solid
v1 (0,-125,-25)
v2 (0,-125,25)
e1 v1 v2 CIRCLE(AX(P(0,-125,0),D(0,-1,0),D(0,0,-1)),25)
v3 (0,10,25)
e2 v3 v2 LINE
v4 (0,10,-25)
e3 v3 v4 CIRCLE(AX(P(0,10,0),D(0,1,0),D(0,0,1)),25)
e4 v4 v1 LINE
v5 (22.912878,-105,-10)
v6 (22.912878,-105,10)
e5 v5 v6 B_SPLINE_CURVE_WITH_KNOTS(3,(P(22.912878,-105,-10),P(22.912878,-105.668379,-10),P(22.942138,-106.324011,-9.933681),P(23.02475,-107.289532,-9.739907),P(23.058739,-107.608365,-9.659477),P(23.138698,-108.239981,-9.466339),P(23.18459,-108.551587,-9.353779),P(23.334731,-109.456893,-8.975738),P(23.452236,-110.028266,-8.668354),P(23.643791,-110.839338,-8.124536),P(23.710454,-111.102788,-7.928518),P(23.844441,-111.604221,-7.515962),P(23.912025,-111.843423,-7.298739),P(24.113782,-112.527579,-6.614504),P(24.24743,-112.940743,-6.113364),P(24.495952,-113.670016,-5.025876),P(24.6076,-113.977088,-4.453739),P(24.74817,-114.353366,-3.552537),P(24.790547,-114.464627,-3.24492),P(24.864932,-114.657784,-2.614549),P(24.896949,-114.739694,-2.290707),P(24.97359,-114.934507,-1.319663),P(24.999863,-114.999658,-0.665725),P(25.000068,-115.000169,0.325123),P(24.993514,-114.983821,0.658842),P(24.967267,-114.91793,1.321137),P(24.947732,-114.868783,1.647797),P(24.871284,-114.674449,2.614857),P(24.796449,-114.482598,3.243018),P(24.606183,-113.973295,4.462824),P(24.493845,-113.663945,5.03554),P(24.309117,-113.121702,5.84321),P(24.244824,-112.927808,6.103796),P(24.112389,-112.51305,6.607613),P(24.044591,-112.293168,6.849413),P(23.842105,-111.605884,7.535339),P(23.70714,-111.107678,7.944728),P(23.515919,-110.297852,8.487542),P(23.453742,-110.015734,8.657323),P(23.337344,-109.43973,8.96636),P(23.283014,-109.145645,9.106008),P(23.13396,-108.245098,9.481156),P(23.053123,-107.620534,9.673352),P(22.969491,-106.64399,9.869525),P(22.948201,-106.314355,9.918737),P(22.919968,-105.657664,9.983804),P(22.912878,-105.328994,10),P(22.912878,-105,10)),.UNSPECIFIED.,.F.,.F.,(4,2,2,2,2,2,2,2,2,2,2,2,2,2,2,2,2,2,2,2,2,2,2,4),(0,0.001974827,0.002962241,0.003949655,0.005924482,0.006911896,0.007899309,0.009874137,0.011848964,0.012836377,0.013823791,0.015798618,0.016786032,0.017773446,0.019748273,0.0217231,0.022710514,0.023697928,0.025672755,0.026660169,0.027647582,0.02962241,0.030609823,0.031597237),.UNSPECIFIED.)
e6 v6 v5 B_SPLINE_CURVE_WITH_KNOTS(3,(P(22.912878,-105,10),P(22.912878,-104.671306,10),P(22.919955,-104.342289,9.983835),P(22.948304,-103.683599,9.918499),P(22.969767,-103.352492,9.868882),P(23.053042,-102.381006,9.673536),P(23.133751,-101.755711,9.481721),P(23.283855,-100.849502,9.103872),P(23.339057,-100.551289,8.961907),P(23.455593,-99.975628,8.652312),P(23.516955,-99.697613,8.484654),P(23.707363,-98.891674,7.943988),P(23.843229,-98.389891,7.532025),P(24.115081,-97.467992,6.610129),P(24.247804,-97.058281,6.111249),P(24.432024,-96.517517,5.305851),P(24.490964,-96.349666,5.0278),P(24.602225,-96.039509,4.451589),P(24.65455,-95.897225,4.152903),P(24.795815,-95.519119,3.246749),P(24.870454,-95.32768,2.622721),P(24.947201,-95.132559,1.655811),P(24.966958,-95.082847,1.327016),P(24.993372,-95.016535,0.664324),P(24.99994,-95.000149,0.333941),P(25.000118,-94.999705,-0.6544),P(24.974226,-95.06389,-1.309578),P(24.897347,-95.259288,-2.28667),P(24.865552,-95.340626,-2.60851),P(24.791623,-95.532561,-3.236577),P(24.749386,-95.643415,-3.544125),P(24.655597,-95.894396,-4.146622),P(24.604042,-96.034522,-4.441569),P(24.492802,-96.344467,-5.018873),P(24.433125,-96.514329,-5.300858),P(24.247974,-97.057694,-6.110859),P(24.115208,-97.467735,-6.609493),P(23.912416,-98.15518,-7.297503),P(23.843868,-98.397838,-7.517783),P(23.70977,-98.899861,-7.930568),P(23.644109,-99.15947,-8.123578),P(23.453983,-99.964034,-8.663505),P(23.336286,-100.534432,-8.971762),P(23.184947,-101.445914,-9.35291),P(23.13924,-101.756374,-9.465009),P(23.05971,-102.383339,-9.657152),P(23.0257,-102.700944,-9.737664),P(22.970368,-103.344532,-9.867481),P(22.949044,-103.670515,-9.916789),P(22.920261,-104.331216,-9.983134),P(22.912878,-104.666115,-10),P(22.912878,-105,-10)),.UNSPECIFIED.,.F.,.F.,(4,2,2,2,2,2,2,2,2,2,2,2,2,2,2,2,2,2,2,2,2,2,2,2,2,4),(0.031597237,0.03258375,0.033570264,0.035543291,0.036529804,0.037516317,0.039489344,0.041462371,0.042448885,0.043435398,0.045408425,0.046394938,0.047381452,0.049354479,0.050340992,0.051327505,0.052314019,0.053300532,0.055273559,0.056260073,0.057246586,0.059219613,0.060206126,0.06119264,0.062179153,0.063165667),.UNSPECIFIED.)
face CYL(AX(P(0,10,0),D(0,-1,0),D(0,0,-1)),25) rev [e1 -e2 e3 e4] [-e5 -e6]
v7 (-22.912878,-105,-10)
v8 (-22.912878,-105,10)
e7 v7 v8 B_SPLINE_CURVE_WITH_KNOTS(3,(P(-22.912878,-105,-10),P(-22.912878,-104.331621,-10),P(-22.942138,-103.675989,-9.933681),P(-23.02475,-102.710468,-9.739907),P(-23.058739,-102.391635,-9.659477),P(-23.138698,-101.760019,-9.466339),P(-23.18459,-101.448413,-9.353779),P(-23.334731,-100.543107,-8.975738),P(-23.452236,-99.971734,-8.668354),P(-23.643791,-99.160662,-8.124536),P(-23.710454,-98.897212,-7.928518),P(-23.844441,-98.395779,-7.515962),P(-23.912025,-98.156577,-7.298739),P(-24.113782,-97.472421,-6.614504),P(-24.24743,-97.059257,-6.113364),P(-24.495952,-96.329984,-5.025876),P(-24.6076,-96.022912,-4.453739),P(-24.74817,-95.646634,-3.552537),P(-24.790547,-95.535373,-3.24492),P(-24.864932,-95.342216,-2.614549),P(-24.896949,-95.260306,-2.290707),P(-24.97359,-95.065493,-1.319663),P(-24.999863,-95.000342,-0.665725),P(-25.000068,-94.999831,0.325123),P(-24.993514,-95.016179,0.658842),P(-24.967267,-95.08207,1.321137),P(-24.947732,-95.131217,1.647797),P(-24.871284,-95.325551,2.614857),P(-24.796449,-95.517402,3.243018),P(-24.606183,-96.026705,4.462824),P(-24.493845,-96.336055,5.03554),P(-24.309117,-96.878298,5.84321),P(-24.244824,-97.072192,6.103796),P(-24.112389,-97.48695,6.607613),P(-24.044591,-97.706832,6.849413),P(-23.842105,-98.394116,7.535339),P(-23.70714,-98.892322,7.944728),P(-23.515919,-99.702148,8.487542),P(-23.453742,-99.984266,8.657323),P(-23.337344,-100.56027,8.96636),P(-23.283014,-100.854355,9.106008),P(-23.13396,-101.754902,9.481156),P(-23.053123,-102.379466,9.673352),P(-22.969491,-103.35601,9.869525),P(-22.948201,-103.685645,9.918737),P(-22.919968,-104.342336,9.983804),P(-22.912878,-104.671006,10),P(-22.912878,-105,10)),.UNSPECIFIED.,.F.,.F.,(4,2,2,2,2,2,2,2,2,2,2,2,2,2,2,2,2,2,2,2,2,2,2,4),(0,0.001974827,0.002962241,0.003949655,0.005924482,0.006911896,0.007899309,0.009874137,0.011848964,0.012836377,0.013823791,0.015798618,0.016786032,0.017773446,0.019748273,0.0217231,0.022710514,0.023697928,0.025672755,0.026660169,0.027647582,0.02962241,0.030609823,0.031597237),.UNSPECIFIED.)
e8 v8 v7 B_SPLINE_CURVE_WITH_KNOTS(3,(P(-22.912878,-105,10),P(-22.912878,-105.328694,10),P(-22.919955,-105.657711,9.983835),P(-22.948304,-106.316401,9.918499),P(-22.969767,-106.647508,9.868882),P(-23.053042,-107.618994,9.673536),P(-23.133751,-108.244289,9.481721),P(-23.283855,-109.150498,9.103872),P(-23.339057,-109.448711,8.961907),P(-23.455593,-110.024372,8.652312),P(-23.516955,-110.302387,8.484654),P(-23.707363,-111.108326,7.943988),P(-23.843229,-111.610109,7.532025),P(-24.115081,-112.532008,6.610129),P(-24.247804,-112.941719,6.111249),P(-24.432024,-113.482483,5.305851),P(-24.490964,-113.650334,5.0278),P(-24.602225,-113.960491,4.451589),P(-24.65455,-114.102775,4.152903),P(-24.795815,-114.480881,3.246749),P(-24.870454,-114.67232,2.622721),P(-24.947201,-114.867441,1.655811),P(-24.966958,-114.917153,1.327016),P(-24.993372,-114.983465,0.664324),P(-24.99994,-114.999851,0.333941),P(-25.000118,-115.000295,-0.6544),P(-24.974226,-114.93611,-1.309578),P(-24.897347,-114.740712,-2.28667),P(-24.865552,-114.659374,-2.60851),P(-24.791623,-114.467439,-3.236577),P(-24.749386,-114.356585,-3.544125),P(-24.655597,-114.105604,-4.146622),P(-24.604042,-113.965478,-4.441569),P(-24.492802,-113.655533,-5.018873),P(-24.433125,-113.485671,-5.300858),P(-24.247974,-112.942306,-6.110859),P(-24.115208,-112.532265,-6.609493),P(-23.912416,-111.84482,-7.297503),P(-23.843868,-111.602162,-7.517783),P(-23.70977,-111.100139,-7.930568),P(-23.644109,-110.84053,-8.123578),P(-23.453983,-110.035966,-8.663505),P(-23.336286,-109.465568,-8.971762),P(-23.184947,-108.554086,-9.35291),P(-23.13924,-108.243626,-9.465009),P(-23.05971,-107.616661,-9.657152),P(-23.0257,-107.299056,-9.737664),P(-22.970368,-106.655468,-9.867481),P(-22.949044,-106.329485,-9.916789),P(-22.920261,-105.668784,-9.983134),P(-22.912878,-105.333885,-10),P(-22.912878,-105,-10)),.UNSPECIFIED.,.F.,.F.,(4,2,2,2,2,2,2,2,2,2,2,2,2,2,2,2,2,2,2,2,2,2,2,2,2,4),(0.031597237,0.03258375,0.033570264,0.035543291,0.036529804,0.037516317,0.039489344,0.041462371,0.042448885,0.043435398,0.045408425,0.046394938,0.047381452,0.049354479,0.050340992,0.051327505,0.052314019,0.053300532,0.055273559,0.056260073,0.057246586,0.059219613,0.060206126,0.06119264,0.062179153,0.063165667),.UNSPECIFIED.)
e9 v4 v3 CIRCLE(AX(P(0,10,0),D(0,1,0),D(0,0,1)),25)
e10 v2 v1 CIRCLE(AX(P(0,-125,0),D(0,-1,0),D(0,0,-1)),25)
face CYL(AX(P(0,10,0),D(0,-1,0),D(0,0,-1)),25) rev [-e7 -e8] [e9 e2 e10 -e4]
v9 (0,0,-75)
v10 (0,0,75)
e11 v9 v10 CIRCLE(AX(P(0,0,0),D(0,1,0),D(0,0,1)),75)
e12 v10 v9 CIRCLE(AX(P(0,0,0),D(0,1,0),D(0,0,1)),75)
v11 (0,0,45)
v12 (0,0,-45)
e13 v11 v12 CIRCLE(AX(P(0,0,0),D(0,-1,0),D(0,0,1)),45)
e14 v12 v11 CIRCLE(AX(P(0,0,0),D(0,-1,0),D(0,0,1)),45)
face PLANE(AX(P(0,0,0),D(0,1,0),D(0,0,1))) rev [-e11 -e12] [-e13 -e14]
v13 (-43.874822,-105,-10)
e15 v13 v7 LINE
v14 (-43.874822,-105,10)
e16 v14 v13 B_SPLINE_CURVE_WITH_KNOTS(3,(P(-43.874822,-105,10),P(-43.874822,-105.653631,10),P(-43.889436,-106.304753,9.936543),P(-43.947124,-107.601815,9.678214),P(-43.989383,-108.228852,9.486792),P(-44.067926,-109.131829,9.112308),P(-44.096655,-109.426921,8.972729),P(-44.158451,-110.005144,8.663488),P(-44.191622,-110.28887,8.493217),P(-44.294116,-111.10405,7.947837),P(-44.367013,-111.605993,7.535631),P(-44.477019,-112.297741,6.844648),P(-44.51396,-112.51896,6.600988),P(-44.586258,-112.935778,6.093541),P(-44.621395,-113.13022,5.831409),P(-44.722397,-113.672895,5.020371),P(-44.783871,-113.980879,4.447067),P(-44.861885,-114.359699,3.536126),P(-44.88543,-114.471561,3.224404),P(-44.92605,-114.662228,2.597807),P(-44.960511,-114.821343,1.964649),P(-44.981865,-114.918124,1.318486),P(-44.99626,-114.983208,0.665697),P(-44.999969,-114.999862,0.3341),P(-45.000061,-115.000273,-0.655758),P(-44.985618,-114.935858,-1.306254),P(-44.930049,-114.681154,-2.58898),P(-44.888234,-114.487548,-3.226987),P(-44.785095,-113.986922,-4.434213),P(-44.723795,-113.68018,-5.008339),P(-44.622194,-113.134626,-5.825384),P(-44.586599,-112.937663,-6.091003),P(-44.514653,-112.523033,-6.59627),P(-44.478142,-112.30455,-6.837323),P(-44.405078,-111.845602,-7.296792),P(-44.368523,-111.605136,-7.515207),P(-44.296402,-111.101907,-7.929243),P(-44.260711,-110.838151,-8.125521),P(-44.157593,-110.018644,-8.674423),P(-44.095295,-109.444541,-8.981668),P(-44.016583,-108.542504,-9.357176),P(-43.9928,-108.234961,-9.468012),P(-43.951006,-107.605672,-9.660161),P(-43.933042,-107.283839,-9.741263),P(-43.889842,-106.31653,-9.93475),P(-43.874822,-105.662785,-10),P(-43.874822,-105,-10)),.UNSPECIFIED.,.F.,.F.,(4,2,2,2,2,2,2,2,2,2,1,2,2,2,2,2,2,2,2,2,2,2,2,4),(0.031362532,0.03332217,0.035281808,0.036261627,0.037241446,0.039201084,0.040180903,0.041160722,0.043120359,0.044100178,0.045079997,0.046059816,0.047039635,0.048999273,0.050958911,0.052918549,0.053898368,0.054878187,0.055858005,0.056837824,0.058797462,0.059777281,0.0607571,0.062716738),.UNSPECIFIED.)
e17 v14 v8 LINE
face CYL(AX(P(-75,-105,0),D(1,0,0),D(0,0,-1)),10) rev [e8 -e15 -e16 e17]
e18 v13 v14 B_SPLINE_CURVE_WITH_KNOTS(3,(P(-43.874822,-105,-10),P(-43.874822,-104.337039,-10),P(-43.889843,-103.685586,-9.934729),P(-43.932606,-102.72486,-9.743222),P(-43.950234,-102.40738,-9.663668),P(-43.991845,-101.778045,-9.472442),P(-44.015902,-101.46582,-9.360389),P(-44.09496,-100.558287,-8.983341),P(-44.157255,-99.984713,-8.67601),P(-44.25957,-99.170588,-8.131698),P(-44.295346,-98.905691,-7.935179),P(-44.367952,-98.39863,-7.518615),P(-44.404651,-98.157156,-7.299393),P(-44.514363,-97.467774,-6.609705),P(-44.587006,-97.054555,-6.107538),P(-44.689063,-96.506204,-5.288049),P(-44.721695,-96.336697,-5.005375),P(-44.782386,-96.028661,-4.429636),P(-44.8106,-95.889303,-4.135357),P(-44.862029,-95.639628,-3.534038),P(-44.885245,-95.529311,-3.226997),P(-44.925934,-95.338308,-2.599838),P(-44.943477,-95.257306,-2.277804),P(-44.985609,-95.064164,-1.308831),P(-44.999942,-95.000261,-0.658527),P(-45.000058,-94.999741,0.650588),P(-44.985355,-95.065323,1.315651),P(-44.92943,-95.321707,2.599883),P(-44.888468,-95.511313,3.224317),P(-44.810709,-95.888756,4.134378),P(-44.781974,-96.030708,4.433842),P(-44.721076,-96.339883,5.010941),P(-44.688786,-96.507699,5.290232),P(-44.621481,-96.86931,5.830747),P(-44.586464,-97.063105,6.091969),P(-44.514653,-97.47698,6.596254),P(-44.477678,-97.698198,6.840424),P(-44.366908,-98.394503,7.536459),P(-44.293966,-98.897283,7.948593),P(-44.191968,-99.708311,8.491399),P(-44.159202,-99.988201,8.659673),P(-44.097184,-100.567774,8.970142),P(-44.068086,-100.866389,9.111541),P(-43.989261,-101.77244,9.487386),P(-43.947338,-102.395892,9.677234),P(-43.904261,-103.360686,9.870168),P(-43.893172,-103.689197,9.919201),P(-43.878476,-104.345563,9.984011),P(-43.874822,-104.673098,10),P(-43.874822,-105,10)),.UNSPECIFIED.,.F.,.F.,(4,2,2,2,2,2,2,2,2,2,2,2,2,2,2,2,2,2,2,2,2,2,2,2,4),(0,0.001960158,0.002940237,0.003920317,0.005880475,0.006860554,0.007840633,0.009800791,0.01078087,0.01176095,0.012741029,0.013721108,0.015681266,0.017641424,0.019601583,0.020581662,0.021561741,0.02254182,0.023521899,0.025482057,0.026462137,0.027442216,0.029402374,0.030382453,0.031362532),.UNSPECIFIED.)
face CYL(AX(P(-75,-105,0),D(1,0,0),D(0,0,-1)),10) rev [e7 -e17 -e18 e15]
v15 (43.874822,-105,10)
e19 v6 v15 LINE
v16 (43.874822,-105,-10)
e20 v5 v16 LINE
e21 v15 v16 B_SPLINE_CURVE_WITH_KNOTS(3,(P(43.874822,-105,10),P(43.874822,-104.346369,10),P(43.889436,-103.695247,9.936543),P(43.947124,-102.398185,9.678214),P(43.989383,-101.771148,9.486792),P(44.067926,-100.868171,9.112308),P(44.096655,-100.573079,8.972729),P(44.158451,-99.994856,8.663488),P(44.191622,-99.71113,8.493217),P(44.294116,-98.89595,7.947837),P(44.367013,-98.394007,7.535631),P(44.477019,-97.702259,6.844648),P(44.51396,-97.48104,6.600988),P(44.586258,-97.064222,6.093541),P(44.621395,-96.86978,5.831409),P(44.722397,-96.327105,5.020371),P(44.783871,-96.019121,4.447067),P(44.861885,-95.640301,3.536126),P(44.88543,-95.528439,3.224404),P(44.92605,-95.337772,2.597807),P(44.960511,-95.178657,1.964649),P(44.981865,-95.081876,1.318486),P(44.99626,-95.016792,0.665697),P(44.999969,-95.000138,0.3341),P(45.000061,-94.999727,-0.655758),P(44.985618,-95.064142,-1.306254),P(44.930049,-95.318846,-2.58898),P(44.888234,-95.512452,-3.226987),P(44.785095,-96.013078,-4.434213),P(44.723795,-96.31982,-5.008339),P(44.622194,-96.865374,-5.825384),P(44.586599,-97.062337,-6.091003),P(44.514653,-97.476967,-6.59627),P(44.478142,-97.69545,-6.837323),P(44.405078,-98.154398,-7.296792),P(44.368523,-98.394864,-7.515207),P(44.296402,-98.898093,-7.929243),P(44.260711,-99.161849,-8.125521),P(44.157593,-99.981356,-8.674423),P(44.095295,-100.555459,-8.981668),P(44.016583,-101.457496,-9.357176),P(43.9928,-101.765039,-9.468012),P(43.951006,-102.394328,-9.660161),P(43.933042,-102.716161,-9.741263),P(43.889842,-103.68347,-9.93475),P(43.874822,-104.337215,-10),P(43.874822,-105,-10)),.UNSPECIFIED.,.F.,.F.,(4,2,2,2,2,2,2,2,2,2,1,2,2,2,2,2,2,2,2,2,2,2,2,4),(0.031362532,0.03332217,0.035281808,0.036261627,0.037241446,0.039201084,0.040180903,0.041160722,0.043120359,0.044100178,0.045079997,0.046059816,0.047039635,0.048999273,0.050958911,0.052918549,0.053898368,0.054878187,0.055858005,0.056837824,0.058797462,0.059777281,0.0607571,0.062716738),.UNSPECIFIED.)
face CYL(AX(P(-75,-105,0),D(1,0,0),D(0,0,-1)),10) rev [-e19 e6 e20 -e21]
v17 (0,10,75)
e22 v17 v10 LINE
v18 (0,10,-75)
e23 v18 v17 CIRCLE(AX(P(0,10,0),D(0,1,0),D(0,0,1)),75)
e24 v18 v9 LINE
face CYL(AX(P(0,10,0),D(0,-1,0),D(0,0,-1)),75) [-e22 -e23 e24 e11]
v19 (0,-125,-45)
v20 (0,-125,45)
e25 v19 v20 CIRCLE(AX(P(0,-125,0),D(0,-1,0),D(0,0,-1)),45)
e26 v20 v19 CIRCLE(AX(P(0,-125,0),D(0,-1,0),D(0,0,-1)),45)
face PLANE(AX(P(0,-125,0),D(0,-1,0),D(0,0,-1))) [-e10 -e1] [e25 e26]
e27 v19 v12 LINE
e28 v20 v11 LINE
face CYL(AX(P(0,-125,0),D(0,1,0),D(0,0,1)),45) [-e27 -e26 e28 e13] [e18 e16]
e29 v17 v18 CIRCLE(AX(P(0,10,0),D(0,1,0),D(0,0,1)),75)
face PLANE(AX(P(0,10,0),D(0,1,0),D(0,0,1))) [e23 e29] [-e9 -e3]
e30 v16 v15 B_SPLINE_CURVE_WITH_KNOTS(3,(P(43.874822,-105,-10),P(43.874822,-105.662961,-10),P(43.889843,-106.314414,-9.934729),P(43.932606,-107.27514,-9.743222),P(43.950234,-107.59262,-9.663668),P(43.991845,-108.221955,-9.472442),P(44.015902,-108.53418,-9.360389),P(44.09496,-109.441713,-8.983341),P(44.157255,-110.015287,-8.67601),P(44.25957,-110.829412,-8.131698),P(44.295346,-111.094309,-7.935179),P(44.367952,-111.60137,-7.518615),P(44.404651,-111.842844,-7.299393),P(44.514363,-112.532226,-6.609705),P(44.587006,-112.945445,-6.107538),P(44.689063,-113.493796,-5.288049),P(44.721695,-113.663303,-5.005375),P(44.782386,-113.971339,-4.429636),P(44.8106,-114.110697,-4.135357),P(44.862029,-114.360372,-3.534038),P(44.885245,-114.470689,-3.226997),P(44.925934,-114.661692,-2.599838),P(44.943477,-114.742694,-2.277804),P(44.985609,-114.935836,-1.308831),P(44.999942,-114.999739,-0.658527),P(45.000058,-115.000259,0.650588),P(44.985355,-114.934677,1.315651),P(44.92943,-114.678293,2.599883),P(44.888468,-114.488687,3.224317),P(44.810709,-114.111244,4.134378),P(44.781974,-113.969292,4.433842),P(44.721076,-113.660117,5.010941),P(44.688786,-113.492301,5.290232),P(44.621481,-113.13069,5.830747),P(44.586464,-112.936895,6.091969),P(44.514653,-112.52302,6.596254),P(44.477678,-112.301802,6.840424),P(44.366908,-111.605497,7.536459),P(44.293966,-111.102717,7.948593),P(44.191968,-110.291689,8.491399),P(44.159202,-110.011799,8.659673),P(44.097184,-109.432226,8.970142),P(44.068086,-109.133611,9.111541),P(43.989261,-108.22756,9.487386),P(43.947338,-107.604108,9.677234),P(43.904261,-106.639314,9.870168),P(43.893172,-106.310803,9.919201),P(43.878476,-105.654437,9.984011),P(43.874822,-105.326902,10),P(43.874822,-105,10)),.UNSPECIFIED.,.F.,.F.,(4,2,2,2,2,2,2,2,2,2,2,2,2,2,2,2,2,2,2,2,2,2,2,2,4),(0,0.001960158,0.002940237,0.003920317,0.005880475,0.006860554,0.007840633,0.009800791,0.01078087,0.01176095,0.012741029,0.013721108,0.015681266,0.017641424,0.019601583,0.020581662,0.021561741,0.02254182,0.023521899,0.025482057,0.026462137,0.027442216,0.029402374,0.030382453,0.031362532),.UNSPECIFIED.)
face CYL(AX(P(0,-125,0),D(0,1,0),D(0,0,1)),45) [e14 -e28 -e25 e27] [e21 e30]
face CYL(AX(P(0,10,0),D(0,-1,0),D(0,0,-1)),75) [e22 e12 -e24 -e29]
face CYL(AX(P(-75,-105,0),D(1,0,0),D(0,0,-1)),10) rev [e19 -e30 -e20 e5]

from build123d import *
from build123d.topology import SkipClean

# Parameters (mm, degrees)
SKETCH2_R               = 75
SKETCH2_R_2             = 25
BOSS_EXTRUDE1_DEPTH     = 10
BOSS_EXTRUDE2_START     = 125
SKETCH3_R               = 45
SKETCH3_R_2             = 25
BOSS_EXTRUDE2_DEPTH     = 125
CUT_EXTRUDE1_DEPTH      = 164.935963108
CUT_EXTRUDE1_DEPTH_BACK = 164.935963108
SKETCH4_R               = 10


with BuildPart() as part:
    # Sketch2 → Boss-Extrude1 (new body)
    with BuildSketch(Plane(origin=(0, 0, 0), x_dir=(1, 0, 0), z_dir=(0, 1, 0))):
        with Locations(Location((0, 0, 0), (0, 0, 270))):
            Circle(SKETCH2_R)
        with Locations(Location((0, 0, 0), (0, 0, 270))):
            Circle(SKETCH2_R_2, mode=Mode.SUBTRACT)
    extrude(amount=BOSS_EXTRUDE1_DEPTH)

    # Sketch3 → Boss-Extrude2 (add)
    with SkipClean():  # the faces are left unmerged after this step: merging them gives an invalid solid
        with BuildSketch(Plane.XZ.offset(BOSS_EXTRUDE2_START)):
            with Locations(Location((0, 0, 0), (0, 0, 90))):
                Circle(SKETCH3_R)
            with Locations(Location((0, 0, 0), (0, 0, 270))):
                Circle(SKETCH3_R_2, mode=Mode.SUBTRACT)
        extrude(amount=-BOSS_EXTRUDE2_DEPTH)

    # Sketch4 → Cut-Extrude1 (cut, two sides: drawn at the far end of the back side and taken through both)
    with SkipClean():  # the faces are left unmerged after this step: merging them gives an invalid solid
        with BuildSketch(Plane(origin=(0, 0, 0), x_dir=(0, 0, -1), z_dir=(1, 0, 0)).offset(-CUT_EXTRUDE1_DEPTH_BACK)):
            with Locations((0, -105)):
                Circle(SKETCH4_R)
        extrude(amount=CUT_EXTRUDE1_DEPTH + CUT_EXTRUDE1_DEPTH_BACK, mode=Mode.SUBTRACT)


solid = part.part
